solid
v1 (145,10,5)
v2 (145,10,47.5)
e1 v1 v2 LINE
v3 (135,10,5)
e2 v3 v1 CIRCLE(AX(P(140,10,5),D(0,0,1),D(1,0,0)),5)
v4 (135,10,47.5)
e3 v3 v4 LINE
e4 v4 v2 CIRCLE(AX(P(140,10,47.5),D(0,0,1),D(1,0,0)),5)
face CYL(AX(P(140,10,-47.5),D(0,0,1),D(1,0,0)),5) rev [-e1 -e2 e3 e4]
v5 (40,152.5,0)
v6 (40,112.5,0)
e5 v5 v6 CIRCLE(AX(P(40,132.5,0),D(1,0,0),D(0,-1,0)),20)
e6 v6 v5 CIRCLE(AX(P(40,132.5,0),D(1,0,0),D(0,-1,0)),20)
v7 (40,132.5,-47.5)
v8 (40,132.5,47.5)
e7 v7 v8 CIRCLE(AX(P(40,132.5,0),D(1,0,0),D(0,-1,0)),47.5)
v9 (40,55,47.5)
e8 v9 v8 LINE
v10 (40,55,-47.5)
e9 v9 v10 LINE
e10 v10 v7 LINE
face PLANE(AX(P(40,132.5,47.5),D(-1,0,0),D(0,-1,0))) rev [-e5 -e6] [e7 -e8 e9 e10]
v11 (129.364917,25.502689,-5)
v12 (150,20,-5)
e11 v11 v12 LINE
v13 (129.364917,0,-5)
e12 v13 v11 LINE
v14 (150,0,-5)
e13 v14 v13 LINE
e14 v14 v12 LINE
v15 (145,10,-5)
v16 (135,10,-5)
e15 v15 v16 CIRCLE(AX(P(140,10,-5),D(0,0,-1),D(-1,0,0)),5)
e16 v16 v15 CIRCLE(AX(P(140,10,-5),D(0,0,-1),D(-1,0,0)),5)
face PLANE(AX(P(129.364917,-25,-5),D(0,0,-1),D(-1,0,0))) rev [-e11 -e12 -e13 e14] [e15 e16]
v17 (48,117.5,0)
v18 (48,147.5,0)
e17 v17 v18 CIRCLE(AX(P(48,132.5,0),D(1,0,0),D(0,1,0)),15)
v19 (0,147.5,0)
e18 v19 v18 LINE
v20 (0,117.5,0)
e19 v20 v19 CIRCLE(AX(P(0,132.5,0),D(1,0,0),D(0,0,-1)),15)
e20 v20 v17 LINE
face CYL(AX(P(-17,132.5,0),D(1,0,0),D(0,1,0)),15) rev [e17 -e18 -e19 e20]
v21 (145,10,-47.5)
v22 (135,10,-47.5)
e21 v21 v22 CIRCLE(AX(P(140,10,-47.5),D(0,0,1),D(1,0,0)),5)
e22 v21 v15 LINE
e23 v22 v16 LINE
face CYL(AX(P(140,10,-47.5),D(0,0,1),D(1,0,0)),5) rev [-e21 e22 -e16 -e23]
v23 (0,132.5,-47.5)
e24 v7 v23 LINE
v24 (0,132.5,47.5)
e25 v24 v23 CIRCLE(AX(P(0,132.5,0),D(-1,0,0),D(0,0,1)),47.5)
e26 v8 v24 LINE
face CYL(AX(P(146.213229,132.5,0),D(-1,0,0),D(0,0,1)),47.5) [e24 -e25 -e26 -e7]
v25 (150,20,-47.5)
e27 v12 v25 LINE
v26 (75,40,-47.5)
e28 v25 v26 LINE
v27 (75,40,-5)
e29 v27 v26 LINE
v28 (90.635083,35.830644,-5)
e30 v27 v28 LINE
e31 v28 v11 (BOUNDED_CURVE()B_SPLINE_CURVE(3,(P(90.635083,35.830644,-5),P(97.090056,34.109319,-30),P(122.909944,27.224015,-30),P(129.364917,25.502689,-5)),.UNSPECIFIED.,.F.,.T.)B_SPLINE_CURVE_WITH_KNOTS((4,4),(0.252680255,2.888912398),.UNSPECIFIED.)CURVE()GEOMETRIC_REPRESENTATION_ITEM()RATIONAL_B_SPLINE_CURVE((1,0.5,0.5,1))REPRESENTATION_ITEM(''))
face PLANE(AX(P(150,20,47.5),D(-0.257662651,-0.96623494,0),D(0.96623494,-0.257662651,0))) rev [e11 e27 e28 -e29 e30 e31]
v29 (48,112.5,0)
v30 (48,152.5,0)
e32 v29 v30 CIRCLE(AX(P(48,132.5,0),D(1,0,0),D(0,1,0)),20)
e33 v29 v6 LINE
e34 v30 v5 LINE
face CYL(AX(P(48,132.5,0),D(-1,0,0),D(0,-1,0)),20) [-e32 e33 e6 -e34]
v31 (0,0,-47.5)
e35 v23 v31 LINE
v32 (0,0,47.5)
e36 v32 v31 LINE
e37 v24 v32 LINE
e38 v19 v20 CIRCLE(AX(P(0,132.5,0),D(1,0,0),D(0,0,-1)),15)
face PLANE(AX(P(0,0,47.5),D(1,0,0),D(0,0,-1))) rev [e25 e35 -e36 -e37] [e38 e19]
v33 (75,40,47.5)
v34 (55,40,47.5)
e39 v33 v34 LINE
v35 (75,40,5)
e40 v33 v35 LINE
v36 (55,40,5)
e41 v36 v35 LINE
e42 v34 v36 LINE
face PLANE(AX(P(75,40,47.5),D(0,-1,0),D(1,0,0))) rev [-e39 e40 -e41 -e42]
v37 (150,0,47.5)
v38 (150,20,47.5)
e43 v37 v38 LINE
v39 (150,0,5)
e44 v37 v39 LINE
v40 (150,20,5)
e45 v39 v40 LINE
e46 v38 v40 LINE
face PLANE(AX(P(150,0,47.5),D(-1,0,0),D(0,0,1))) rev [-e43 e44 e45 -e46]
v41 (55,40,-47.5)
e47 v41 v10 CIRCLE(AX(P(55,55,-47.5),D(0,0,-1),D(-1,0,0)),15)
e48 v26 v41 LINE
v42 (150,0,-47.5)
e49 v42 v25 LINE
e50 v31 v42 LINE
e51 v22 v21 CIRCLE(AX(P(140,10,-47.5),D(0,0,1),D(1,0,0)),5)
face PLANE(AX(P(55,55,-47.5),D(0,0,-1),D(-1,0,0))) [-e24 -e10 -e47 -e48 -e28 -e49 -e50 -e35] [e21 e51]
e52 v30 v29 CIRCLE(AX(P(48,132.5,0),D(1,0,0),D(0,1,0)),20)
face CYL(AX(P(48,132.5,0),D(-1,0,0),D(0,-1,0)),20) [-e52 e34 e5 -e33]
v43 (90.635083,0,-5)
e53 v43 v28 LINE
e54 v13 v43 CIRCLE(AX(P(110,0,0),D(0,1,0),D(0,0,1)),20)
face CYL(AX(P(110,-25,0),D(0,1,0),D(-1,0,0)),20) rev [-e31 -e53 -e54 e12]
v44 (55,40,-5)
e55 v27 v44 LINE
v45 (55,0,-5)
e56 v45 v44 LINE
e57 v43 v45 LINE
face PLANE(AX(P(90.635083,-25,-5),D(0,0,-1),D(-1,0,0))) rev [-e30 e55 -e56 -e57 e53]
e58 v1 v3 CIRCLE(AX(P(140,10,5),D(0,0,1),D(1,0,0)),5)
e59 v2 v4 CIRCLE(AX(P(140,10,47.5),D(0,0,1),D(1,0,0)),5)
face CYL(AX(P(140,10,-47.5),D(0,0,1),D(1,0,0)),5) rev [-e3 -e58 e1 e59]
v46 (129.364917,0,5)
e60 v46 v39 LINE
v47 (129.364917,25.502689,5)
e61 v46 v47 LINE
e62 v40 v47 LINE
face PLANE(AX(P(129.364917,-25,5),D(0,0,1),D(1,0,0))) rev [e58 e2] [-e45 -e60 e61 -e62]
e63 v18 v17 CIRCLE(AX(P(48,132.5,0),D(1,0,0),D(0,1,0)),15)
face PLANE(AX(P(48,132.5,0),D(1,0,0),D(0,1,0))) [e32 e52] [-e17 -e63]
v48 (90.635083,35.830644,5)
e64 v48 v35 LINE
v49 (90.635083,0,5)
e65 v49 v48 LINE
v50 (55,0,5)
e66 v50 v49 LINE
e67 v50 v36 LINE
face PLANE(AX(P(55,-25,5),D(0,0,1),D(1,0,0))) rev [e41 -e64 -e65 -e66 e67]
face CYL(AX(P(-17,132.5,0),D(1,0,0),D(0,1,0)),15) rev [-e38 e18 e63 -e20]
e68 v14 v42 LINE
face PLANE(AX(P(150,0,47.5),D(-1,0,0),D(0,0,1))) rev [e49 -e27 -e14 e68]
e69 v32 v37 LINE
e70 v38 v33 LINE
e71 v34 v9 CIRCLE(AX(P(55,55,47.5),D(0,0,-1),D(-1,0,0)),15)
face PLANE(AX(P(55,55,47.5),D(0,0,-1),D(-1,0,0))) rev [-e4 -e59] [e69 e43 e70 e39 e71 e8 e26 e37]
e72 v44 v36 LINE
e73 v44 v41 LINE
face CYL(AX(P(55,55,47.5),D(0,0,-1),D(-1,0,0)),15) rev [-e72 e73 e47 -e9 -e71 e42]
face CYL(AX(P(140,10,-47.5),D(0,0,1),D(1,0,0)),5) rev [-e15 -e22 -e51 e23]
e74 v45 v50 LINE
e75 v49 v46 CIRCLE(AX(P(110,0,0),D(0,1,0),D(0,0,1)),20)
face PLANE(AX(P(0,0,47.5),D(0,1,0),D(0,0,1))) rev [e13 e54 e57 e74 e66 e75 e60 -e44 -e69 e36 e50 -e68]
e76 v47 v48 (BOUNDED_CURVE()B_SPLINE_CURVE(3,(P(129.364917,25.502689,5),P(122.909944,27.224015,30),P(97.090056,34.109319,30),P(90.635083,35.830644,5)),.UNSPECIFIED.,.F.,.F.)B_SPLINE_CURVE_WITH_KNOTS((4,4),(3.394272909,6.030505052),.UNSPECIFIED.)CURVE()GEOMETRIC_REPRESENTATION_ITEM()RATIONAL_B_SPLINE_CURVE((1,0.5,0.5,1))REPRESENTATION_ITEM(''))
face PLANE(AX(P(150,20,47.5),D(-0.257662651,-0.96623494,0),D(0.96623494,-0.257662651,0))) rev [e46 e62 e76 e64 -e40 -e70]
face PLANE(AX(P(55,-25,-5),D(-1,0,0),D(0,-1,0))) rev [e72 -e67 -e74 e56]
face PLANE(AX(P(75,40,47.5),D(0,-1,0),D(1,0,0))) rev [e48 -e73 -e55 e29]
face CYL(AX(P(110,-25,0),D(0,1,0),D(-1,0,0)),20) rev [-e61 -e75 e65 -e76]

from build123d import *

# Parameters (mm, degrees)
L_BRACKET_BODY_DEPTH          = 47.5
UPRIGHT_ROUND_TOP_DEPTH       = 40
HUB_BOSS_40_SKETCH_R          = 20
HUB_BOSS_40_DEPTH             = 8
BEARING_BORE_30_SKETCH_R      = 15
BEARING_BORE_30_DEPTH         = 65
CLAMP_BORE_40_WITH_SLOT_DEPTH = 65
CLAMP_SCREW_HOLE_10_SKETCH_R  = 5
CLAMP_SCREW_HOLE_10_DEPTH     = 253.833937595


with BuildPart() as part:
    # L-Bracket Profile Sketch → L-Bracket Body (new, symmetric)
    with BuildSketch(Plane.XY):
        with BuildLine():
            Line((0, 0), (150, 0))
            Line((150, 0), (150, 20))
            Line((150, 20), (75, 40))
            Line((75, 40), (55, 40))
            ThreePointArc((55, 40), (44.393398282, 44.393398282), (40, 55))
            Line((40, 55), (40, 132.5))
            Line((40, 132.5), (0, 132.5))
            Line((0, 132.5), (0, 0))
        make_face()
    extrude(amount=L_BRACKET_BODY_DEPTH, both=True)

    # Upright Round Top Sketch → Upright Round Top (add)
    with BuildSketch(Plane.ZY):
        with BuildLine():
            Line((-47.5, 132.5), (47.5, 132.5))
            ThreePointArc((47.5, 132.5), (0, 180), (-47.5, 132.5))
        make_face()
    extrude(amount=-UPRIGHT_ROUND_TOP_DEPTH)

    # Hub Boss Ø40 Sketch → Hub Boss Ø40 (add)
    with BuildSketch(Plane(origin=(40, 0, 0), x_dir=(0, 0, -1), z_dir=(1, 0, 0))):
        with Locations(Location((0, 132.5, 0), (0, 0, 270))):
            Circle(HUB_BOSS_40_SKETCH_R)
    extrude(amount=HUB_BOSS_40_DEPTH)

    # Bearing Bore Ø30 Sketch → Bearing Bore Ø30 (cut)
    with BuildSketch(Plane(origin=(48, 0, 0), x_dir=(0, 0, -1), z_dir=(1, 0, 0))):
        with Locations(Location((0, 132.5, 0), (0, 0, 90))):
            Circle(BEARING_BORE_30_SKETCH_R)
    extrude(amount=-BEARING_BORE_30_DEPTH, mode=Mode.SUBTRACT)

    # Clamp Bore Ø40 Slot Sketch → Clamp Bore Ø40 with Slot (cut)
    with BuildSketch(Plane(origin=(0, 40, 0), x_dir=(1, 0, 0), z_dir=(0, 1, 0))):
        with BuildLine():
            Line((150, 5), (150, -5))
            Line((150, -5), (129.364916731, -5))
            ThreePointArc((129.364916731, -5), (110, -20), (90.635083269, -5))
            Line((90.635083269, -5), (55, -5))
            Line((55, -5), (55, 5))
            Line((55, 5), (90.635083269, 5))
            ThreePointArc((90.635083269, 5), (110, 20), (129.364916731, 5))
            Line((129.364916731, 5), (150, 5))
        make_face()
    extrude(amount=-CLAMP_BORE_40_WITH_SLOT_DEPTH, mode=Mode.SUBTRACT)

    # Clamp Screw Hole Ø10 Sketch → Clamp Screw Hole Ø10 (cut, through all)
    with BuildSketch(Plane.XY.offset(47.5)):
        with Locations((140, 10)):
            Circle(CLAMP_SCREW_HOLE_10_SKETCH_R)
    extrude(amount=-CLAMP_SCREW_HOLE_10_DEPTH, mode=Mode.SUBTRACT)


solid = part.part
